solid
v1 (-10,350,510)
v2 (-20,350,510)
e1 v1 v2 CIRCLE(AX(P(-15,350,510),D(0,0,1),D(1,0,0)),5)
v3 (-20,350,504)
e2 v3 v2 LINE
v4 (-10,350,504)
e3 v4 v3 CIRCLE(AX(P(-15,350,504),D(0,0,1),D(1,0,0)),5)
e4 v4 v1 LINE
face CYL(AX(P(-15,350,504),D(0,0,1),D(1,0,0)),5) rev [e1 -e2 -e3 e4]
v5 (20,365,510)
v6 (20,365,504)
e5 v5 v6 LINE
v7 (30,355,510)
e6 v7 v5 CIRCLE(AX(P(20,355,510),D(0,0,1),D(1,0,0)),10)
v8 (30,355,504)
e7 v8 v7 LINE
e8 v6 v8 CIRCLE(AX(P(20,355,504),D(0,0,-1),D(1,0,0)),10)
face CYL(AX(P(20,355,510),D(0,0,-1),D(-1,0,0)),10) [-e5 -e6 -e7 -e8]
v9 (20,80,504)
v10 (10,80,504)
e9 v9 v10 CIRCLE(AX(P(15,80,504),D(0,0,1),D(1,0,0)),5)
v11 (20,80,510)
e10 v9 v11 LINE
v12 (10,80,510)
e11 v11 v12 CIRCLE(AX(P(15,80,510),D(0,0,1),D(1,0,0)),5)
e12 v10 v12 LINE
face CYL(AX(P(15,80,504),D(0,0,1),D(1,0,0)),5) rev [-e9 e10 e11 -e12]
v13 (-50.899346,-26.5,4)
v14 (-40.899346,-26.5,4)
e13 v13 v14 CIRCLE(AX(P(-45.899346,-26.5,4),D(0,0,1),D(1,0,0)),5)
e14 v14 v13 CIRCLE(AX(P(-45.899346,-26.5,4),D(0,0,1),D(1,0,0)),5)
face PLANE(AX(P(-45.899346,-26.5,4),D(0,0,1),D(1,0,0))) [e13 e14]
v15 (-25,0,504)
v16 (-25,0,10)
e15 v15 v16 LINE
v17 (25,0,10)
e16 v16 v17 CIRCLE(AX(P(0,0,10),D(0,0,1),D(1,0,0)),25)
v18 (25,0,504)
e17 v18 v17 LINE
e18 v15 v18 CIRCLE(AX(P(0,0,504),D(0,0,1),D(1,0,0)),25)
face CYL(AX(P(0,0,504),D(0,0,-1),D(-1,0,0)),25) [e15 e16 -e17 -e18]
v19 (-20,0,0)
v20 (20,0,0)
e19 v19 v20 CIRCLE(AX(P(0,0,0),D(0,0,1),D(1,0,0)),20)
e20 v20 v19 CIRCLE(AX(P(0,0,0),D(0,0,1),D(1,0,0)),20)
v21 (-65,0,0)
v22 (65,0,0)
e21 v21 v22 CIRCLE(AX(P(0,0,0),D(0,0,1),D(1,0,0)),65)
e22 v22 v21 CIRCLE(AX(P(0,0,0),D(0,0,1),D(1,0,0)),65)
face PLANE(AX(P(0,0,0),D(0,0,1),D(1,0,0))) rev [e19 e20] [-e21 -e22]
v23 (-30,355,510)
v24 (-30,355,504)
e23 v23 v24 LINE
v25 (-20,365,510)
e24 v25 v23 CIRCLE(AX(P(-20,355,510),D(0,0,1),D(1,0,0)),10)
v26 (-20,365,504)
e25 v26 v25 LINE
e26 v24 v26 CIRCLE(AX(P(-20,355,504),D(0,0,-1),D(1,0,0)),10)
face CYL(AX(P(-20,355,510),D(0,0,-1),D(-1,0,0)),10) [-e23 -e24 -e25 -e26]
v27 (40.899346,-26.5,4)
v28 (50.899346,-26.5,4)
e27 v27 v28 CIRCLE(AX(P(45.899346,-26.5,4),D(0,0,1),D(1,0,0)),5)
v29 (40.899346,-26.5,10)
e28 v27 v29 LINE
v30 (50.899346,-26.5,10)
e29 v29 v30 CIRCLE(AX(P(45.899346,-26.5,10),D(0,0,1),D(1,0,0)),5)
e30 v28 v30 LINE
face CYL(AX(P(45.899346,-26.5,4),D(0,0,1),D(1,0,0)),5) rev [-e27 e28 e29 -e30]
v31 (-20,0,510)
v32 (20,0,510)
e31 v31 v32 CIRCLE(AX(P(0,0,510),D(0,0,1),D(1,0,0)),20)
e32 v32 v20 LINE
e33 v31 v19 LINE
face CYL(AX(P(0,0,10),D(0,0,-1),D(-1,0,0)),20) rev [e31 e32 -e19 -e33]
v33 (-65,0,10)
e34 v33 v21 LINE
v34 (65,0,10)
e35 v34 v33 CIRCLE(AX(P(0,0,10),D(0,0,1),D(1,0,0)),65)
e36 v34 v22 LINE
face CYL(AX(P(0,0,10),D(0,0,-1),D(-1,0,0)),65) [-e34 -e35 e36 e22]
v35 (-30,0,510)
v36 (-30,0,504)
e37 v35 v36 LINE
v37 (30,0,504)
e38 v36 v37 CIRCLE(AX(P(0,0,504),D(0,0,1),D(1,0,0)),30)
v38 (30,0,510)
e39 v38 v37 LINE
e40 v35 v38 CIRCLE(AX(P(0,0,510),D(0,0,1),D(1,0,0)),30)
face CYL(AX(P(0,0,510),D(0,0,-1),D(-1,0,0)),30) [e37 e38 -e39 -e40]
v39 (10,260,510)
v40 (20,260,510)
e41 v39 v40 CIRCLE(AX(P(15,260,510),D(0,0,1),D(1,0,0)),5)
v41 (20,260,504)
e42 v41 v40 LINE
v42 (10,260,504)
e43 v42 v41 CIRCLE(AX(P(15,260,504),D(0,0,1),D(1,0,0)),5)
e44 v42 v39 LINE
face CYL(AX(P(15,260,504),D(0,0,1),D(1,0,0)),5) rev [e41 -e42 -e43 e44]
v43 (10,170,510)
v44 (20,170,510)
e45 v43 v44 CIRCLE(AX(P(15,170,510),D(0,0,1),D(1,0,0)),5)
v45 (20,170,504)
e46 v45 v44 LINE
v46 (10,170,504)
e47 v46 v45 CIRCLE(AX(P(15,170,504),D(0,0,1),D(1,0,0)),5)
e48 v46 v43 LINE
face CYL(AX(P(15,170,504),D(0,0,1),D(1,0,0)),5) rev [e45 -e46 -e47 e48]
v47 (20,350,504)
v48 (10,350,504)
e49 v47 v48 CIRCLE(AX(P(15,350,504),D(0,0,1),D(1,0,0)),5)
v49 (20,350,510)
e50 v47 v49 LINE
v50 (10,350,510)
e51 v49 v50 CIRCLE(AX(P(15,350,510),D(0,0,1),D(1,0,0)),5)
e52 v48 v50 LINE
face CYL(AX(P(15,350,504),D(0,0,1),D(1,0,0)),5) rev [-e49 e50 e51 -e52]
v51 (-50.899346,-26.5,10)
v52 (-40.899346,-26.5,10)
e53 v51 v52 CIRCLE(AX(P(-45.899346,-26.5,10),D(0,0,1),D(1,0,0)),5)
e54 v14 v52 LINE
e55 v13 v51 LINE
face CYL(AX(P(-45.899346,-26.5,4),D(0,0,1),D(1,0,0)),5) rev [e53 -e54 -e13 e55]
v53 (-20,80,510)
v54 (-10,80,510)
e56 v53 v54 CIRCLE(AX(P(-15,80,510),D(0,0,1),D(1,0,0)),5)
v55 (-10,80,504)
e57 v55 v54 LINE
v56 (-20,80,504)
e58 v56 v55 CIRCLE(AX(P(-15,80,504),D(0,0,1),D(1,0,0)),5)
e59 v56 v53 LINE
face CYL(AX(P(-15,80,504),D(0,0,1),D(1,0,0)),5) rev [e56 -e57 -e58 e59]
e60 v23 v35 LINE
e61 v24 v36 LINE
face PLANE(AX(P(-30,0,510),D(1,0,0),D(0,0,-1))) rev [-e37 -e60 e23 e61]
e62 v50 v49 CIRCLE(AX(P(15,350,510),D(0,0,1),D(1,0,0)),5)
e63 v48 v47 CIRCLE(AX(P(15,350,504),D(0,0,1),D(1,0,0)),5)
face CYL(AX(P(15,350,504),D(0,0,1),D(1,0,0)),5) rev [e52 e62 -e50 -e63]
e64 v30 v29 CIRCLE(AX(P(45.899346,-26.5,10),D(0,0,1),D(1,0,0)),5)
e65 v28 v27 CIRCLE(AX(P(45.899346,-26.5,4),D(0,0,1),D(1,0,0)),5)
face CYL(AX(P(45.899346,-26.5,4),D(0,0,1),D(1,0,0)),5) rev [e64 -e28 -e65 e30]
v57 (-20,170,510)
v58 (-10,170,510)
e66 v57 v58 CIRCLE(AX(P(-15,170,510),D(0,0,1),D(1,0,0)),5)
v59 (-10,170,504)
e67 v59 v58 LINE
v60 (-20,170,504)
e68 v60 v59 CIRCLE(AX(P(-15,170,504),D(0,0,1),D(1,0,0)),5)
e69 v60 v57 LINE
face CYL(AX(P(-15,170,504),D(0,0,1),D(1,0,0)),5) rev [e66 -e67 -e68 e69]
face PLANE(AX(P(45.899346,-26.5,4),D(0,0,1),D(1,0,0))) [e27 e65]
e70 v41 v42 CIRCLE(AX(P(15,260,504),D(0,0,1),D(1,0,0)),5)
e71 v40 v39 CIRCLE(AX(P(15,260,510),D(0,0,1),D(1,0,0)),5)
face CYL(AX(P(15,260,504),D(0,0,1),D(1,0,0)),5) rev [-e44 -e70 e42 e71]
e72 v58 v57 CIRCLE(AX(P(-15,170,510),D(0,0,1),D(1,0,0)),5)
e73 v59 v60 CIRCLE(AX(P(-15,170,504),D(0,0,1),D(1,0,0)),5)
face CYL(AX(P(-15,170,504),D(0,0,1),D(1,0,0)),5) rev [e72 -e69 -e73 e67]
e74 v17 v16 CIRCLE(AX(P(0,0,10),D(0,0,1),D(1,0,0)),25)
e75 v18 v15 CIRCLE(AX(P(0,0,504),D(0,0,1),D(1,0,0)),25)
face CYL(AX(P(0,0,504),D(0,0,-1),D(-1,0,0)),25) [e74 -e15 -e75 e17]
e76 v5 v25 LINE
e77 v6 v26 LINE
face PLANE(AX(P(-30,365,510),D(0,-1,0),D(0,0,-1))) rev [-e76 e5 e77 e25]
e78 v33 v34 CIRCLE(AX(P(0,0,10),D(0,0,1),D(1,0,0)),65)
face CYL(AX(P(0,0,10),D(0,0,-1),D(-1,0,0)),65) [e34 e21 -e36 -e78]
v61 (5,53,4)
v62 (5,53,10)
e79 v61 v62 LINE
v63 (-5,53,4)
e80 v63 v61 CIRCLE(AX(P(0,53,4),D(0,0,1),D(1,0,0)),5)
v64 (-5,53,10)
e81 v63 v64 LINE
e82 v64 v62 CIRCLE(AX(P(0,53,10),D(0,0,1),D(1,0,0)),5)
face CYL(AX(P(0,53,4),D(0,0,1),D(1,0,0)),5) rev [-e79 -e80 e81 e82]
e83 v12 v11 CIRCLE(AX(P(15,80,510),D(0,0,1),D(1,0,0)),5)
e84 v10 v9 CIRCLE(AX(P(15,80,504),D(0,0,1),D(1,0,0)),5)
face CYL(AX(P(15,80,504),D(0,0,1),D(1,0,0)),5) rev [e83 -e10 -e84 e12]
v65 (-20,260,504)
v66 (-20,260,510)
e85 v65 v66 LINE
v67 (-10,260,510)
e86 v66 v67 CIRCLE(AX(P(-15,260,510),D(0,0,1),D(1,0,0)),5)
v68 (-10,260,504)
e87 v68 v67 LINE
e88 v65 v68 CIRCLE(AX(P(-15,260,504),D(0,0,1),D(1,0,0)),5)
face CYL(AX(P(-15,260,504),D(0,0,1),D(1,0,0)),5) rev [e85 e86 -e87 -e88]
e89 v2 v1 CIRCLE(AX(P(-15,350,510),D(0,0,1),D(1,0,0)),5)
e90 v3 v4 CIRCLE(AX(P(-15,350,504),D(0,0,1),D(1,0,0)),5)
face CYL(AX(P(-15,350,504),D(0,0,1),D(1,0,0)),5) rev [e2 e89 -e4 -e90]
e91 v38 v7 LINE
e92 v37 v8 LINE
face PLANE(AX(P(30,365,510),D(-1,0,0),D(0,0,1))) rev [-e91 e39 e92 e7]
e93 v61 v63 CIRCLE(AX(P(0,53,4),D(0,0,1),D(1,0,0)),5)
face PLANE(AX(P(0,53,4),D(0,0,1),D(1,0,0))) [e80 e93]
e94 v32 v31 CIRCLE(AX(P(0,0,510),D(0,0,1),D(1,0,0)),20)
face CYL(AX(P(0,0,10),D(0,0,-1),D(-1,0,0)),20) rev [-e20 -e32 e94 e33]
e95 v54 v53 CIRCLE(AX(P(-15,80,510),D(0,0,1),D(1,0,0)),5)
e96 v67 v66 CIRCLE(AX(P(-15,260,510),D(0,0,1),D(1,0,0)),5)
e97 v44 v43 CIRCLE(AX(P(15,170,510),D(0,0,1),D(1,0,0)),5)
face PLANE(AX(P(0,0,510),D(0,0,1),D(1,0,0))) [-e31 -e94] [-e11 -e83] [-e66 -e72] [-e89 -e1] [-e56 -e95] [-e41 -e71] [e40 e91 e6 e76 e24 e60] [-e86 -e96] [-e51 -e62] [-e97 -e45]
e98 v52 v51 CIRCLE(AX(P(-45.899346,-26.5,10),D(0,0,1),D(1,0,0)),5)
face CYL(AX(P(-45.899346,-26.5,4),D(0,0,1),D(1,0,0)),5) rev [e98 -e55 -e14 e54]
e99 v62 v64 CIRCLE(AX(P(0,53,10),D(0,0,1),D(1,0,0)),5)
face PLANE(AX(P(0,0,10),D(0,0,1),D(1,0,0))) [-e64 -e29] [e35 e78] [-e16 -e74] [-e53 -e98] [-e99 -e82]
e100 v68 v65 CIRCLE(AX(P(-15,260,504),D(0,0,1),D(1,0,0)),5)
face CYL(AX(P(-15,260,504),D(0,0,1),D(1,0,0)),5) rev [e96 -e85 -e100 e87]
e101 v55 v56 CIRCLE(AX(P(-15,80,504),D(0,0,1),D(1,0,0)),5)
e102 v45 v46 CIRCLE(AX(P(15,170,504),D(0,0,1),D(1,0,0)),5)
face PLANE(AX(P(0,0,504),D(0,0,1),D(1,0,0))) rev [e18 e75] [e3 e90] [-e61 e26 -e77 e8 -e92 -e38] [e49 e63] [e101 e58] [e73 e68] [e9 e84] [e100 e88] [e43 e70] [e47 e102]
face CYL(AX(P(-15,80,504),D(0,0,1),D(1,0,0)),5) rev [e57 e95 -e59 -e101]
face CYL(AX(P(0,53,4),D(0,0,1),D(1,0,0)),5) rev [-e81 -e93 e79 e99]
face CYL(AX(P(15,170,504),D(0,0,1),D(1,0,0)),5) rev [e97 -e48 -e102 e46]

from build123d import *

# Parameters (mm, degrees)
SKETCH1_R           = 65
SKETCH1_R_2         = 20
BOSS_EXTRUDE1_DEPTH = 10
SKETCH2_R           = 25
SKETCH2_R_2         = 20
BOSS_EXTRUDE2_DEPTH = 494
SKETCH3_R           = 20
BOSS_EXTRUDE3_DEPTH = 6
FILLET1_R           = 10
SKETCH4_R           = 5
CUT_EXTRUDE1_DEPTH  = 6
SKETCH5_R           = 5
CUT_EXTRUDE2_DEPTH  = 6


with BuildPart() as part:
    # Sketch1 → Boss-Extrude1 (new body)
    with BuildSketch(Plane.XY):
        Circle(SKETCH1_R)
        Circle(SKETCH1_R_2, mode=Mode.SUBTRACT)
    extrude(amount=BOSS_EXTRUDE1_DEPTH)

    # Sketch2 → Boss-Extrude2 (add)
    with BuildSketch(Plane.XY.offset(10)):
        Circle(SKETCH2_R)
        Circle(SKETCH2_R_2, mode=Mode.SUBTRACT)
    extrude(amount=BOSS_EXTRUDE2_DEPTH)

    # Sketch3 → Boss-Extrude3 (add)
    with BuildSketch(Plane.XY.offset(504)):
        with BuildLine():
            Line((-30, 0), (-30, 365))
            Line((-30, 365), (30, 365))
            Line((30, 365), (30, 0))
            ThreePointArc((30, 0), (0, -30), (-30, 0))
        make_face()
        Circle(SKETCH3_R, mode=Mode.SUBTRACT)
    extrude(amount=BOSS_EXTRUDE3_DEPTH)

    # Fillet1
    fillet1_edges = [part.edges().sort_by_distance(p)[0] for p in [
        (30, 365, 507),
        (-30, 365, 507),
    ]]
    fillet(fillet1_edges, radius=FILLET1_R)

    # Sketch4 → Cut-Extrude1 (cut)
    with BuildSketch(Plane.XY.offset(510)):
        with Locations((-15, 350)):
            Circle(SKETCH4_R)
        with Locations((15, 350)):
            Circle(SKETCH4_R)
        with Locations((-15, 260)):
            Circle(SKETCH4_R)
        with Locations((15, 260)):
            Circle(SKETCH4_R)
        with Locations((-15, 170)):
            Circle(SKETCH4_R)
        with Locations((15, 170)):
            Circle(SKETCH4_R)
        with Locations((-15, 80)):
            Circle(SKETCH4_R)
        with Locations((15, 80)):
            Circle(SKETCH4_R)
    extrude(amount=-CUT_EXTRUDE1_DEPTH, mode=Mode.SUBTRACT)

    # Sketch5 → Cut-Extrude2 (cut)
    with BuildSketch(Plane.XY.offset(10)):
        with Locations((0, 53)):
            Circle(SKETCH5_R)
        with Locations((45.899346401, -26.5)):
            Circle(SKETCH5_R)
        with Locations((-45.899346401, -26.5)):
            Circle(SKETCH5_R)
    extrude(amount=-CUT_EXTRUDE2_DEPTH, mode=Mode.SUBTRACT)


solid = part.part
